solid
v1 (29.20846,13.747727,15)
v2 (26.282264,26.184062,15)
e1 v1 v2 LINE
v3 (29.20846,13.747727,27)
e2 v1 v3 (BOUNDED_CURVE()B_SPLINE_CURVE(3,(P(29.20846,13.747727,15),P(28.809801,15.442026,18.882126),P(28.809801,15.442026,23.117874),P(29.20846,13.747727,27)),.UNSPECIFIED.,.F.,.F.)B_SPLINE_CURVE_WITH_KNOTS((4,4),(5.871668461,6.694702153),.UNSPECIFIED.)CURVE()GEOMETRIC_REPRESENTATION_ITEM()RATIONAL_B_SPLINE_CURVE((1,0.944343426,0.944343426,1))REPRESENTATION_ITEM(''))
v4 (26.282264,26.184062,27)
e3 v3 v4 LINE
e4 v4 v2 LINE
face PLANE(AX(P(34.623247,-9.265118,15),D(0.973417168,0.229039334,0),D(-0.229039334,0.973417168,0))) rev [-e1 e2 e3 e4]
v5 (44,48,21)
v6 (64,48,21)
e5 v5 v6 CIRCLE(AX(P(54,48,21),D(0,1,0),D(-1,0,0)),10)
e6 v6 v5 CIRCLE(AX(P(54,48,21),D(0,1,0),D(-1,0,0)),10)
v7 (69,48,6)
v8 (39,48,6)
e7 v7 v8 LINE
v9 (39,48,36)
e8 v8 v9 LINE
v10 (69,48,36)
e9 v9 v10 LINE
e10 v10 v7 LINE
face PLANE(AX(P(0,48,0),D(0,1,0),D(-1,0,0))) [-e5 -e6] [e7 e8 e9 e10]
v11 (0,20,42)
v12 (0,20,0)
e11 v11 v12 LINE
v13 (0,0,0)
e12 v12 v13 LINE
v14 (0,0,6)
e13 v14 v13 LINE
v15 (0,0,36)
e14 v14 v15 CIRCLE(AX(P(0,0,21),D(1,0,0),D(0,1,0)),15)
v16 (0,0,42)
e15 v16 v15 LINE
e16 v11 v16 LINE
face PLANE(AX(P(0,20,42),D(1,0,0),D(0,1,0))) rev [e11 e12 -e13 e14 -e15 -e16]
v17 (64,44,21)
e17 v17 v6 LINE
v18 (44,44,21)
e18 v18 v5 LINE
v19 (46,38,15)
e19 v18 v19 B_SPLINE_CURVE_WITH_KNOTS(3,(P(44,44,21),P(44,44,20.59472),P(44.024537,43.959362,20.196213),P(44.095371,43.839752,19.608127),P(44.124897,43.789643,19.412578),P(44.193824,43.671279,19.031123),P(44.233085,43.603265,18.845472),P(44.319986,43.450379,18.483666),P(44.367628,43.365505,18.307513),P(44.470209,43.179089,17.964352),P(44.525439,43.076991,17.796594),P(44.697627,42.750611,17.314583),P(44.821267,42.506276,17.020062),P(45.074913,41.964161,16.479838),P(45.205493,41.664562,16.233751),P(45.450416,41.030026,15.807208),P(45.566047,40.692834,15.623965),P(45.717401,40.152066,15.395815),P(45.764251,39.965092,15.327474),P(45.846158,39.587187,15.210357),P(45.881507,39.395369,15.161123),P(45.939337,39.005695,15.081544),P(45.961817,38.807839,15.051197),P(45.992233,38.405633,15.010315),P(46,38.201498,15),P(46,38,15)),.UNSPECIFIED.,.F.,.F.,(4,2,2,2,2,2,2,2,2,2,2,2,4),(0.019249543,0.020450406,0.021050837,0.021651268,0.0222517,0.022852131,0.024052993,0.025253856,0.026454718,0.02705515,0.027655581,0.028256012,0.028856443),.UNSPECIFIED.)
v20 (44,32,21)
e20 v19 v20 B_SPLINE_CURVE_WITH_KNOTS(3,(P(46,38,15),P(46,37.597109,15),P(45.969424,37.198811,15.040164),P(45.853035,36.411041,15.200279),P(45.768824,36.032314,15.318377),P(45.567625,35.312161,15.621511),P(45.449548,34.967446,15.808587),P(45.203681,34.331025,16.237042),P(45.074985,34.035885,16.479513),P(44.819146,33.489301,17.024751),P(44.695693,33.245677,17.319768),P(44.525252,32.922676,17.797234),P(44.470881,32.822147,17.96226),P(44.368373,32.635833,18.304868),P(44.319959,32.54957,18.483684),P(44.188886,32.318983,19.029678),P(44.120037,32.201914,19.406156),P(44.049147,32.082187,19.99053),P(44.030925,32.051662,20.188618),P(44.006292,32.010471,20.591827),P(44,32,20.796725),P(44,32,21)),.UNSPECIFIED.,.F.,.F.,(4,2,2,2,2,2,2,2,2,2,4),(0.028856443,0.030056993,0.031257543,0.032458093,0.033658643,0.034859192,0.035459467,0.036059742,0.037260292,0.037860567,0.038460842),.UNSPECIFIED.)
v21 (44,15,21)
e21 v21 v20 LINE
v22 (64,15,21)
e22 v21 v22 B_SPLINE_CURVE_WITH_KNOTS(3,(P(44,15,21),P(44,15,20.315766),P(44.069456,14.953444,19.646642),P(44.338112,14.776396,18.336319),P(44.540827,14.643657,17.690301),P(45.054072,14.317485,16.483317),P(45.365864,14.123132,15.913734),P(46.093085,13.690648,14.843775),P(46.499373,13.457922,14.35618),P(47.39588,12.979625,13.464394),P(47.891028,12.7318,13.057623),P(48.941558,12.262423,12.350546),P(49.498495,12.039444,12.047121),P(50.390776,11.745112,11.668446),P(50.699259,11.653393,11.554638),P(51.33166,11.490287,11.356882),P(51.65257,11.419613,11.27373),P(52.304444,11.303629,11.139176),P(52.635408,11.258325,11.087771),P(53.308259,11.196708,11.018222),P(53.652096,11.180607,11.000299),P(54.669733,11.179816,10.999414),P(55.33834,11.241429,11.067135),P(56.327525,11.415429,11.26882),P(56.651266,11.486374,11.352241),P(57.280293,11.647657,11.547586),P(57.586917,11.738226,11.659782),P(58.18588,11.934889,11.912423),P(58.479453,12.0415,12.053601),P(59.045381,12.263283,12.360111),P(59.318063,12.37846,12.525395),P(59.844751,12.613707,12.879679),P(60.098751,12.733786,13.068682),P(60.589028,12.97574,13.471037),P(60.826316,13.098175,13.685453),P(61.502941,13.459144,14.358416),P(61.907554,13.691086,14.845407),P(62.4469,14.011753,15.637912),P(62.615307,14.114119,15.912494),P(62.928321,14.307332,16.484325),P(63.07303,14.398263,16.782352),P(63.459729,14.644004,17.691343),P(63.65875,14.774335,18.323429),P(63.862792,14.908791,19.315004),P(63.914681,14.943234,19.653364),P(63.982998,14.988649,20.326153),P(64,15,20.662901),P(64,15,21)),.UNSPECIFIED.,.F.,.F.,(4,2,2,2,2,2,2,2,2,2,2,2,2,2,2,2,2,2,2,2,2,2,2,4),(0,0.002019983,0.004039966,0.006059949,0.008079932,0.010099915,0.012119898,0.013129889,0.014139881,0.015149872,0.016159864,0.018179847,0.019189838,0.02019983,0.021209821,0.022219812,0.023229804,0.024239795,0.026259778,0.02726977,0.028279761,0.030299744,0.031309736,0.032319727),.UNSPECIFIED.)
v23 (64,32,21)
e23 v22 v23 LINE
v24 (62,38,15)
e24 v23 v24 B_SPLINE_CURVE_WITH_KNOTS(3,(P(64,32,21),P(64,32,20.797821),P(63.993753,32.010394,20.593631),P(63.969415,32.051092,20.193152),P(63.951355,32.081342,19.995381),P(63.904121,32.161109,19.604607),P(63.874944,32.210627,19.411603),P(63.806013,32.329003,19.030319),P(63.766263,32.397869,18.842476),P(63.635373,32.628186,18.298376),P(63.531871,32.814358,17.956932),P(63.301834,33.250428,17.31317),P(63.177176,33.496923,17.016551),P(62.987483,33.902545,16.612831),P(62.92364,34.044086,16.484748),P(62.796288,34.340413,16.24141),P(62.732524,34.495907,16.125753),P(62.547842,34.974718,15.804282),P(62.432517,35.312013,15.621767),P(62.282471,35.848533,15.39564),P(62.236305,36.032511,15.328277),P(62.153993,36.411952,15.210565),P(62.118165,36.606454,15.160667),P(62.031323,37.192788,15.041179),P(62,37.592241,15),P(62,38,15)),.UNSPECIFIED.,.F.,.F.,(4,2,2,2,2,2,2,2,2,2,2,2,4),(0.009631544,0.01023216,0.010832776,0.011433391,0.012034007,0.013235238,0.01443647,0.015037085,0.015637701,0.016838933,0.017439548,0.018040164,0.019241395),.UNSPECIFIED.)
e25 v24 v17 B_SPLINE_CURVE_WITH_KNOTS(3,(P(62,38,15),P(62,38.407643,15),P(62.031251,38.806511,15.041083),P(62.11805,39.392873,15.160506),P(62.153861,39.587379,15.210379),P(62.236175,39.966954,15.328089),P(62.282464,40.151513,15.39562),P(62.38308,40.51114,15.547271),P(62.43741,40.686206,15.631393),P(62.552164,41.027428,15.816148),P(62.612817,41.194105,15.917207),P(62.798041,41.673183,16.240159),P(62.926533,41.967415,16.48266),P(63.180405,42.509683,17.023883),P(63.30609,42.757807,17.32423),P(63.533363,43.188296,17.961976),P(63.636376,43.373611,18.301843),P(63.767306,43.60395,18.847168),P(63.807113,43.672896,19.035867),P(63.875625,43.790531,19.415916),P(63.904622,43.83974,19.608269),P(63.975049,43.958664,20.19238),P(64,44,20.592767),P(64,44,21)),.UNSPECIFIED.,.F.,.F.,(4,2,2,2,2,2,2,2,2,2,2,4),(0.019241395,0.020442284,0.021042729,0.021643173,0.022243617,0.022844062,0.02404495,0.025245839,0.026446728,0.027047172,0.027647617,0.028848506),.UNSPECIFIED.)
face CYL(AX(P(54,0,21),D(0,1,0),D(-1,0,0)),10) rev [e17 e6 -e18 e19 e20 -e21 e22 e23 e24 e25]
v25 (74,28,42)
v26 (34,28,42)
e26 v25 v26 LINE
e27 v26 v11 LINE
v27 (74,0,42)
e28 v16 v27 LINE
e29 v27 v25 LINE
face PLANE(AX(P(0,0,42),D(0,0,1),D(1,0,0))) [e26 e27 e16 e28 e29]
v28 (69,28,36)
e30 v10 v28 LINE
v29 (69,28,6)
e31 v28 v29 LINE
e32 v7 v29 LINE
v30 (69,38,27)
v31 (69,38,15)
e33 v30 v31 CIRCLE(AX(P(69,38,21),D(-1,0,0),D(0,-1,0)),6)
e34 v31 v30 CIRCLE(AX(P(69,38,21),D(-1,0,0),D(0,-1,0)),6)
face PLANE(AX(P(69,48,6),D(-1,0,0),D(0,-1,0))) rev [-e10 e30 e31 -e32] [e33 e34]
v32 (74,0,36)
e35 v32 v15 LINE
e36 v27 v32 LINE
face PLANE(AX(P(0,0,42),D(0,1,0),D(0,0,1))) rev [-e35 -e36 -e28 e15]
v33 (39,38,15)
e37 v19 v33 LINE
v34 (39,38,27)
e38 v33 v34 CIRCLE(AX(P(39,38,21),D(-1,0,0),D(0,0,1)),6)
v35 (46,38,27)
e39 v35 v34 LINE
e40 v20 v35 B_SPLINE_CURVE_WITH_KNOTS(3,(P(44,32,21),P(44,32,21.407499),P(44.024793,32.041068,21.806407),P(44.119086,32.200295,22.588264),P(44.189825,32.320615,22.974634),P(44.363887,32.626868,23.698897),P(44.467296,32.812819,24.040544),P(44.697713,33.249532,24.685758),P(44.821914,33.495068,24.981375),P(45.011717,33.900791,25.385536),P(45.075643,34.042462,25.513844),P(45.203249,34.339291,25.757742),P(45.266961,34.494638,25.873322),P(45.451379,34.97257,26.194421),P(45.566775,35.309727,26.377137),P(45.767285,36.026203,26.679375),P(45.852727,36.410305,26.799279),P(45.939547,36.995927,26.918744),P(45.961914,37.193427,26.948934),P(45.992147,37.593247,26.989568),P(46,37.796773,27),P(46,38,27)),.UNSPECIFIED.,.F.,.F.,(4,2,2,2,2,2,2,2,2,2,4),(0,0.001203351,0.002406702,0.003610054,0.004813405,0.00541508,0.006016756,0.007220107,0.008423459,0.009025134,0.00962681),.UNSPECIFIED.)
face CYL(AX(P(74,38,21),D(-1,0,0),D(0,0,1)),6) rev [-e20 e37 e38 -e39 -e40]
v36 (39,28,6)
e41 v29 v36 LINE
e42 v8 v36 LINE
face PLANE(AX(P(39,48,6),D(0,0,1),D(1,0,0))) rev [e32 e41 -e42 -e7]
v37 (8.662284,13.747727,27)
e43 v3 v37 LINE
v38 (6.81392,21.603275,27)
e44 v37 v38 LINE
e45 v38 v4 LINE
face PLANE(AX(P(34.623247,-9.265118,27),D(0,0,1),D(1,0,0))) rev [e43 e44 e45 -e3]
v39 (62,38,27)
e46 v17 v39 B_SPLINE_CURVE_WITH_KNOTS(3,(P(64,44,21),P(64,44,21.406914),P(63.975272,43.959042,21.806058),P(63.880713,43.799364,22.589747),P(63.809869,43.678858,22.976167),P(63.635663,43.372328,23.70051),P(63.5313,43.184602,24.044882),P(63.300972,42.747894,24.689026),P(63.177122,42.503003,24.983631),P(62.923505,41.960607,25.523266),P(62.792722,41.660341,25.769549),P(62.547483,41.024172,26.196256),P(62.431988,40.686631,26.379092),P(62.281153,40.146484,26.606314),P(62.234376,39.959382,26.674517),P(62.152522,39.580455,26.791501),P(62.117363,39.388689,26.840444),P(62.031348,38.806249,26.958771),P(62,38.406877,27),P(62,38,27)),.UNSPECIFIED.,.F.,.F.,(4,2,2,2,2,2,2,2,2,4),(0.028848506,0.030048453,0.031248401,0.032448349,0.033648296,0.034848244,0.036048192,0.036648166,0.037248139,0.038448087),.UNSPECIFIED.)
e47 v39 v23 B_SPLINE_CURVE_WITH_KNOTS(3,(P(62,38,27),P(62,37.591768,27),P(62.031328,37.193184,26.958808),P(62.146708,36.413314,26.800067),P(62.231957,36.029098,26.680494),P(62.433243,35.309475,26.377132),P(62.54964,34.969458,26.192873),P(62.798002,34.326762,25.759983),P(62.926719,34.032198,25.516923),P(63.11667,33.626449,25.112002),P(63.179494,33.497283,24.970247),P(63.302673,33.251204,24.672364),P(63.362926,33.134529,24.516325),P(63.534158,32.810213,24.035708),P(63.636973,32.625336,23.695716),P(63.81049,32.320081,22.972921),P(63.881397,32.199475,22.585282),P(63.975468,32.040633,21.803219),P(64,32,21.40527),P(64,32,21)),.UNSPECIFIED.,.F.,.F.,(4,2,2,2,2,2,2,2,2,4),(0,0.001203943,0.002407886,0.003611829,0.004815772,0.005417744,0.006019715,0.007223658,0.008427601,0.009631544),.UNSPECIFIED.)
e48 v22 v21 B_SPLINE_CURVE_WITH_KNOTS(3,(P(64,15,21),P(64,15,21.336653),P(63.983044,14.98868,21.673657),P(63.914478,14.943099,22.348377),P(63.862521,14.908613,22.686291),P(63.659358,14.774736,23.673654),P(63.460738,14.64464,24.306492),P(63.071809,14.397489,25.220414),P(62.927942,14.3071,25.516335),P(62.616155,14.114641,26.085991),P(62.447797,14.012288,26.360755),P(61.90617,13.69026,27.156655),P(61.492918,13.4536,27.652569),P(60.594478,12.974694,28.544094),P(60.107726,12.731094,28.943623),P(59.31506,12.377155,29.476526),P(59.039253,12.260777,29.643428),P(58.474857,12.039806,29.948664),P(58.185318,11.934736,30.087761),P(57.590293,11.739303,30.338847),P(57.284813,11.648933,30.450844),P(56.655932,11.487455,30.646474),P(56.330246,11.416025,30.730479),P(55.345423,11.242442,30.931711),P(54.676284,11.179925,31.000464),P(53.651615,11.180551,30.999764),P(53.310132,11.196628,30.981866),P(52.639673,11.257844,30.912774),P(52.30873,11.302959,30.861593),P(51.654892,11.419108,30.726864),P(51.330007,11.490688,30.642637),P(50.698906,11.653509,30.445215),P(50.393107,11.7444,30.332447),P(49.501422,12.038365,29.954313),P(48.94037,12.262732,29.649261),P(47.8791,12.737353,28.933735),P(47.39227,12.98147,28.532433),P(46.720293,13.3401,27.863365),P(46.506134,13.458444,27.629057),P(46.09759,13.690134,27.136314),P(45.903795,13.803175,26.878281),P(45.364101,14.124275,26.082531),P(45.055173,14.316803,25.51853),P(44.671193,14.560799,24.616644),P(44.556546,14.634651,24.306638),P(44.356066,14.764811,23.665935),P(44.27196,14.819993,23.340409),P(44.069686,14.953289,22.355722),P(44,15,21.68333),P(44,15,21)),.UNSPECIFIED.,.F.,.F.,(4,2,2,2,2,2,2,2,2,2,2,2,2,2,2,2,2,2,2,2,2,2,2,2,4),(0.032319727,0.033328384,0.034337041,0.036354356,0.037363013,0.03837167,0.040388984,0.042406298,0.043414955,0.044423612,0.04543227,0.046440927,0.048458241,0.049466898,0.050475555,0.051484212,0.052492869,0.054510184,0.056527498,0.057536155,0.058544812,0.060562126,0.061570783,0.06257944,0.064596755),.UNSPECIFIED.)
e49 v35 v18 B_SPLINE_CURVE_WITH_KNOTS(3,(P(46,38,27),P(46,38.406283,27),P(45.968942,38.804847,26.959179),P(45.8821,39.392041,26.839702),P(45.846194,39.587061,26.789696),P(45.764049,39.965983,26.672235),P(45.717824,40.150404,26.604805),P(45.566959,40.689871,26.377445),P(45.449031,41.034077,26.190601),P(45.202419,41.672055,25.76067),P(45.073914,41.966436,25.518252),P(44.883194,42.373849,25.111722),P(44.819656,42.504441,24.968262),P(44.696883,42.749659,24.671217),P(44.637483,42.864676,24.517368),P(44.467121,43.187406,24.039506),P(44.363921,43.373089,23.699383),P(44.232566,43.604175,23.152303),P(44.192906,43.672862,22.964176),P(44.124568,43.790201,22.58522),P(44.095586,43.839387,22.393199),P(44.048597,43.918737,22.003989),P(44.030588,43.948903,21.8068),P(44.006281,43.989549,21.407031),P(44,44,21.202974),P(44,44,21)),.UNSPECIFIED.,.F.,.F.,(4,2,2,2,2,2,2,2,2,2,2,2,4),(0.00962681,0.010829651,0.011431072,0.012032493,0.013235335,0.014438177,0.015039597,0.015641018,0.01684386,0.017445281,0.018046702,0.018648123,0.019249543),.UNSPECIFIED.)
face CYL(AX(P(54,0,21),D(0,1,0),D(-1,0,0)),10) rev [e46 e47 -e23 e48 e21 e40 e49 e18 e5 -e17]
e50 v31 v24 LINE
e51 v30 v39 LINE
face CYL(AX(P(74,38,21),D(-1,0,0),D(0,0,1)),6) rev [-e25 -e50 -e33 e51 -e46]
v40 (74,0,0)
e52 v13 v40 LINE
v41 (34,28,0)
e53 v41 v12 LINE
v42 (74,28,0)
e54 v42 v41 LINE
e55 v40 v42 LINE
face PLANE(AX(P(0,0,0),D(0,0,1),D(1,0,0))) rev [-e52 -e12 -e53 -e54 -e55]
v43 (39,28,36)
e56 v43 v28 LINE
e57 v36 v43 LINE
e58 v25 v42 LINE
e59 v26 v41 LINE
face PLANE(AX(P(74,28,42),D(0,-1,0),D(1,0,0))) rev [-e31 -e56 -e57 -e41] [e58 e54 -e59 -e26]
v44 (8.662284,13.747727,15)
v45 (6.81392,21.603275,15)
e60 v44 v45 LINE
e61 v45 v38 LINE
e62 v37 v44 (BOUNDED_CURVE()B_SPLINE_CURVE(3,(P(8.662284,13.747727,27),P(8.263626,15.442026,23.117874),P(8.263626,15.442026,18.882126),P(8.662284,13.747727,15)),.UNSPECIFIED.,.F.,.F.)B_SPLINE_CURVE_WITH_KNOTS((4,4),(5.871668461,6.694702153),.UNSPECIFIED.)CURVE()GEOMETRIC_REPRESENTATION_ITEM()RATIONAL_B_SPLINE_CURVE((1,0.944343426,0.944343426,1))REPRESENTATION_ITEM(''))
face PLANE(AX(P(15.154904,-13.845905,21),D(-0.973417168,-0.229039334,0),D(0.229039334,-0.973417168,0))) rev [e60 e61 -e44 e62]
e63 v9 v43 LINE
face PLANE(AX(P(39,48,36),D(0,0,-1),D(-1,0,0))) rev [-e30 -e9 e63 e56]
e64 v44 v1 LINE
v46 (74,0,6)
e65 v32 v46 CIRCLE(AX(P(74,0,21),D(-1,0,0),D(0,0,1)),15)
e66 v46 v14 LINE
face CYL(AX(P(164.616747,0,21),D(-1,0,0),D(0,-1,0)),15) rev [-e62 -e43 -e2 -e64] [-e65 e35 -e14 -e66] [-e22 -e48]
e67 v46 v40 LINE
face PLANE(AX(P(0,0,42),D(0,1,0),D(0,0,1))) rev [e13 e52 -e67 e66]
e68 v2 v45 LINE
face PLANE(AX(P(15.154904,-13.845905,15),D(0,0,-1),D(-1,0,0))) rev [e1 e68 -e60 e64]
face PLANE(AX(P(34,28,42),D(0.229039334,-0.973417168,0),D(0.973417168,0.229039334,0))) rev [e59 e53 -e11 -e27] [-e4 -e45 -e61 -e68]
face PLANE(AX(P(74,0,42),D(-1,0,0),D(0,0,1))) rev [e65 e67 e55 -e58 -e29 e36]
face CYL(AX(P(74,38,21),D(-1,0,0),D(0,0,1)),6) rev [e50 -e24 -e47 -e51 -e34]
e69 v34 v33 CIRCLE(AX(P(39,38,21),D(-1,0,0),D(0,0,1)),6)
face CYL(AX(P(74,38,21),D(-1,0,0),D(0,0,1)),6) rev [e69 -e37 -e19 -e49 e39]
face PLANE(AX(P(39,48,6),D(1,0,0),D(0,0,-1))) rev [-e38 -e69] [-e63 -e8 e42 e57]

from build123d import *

# Parameters (mm, degrees)
BASE_BLOCK_DEPTH       = 42
TOP_BOSS_SKETCH_W      = 30
TOP_BOSS_SKETCH_H      = 30
TOP_BOSS_30X30_DEPTH   = 20
VERTICAL_BORE_SKETCH_R = 10
VERTICAL_BORE_DEPTH    = 98.693397935
CROSS_HOLE_SKETCH_R    = 6
CROSS_HOLE_DEPTH       = 75.759614766
ANGLED_POCKET_DEPTH    = 94.61448679
ARCH_CUTOUT_DEPTH      = 98.693397984
ARCH_CUTOUT_DEPTH_BACK = 98.693397984


with BuildPart() as part:
    # Base Block Profile Sketch → Base Block (new body)
    with BuildSketch(Plane.XY):
        Polygon((0, 0), (74, 0), (74, 28), (34, 28), (0, 20), align=None)
    extrude(amount=BASE_BLOCK_DEPTH)

    # Top Boss Sketch → Top Boss 30x30 (add)
    with BuildSketch(Plane(origin=(0, 28, 0), x_dir=(1, 0, 0), z_dir=(0, 1, 0))):
        with Locations((54, -21)):
            Rectangle(TOP_BOSS_SKETCH_W, TOP_BOSS_SKETCH_H)
    extrude(amount=TOP_BOSS_30X30_DEPTH)

    # Vertical Bore Sketch → Vertical Bore (cut, through all)
    with BuildSketch(Plane(origin=(0, 48, 0), x_dir=(1, 0, 0), z_dir=(0, 1, 0))):
        with Locations(Location((54, -21, 0), (0, 0, 180))):
            Circle(VERTICAL_BORE_SKETCH_R)
    extrude(amount=-VERTICAL_BORE_DEPTH, mode=Mode.SUBTRACT)

    # Cross Hole Sketch → Cross Hole (cut, through all)
    with BuildSketch(Plane.ZY.offset(-39)):
        with Locations((21, 38)):
            Circle(CROSS_HOLE_SKETCH_R)
    extrude(amount=-CROSS_HOLE_DEPTH, mode=Mode.SUBTRACT)

    # Angled Pocket Sketch → Angled Pocket (cut, through all)
    with BuildSketch(Plane(origin=(-4.459016393, 18.950819672, 0), x_dir=(0.973417168333576, 0.22903933372554744, 0), z_dir=(-0.22903933372554744, 0.973417168333576, 0))):
        Polygon((11.580786675, -21), (11.580786675, -15), (31.580786675, -15), (31.580786675, -27), (11.580786675, -27), align=None)
    extrude(amount=-ANGLED_POCKET_DEPTH, mode=Mode.SUBTRACT)

    # Arch Cutout Sketch → Arch Cutout (cut, two sides: drawn at the far end of the back side and taken through both)
    with BuildSketch(Plane.ZY.offset(-ARCH_CUTOUT_DEPTH_BACK)):
        with BuildLine():
            Line((36, -130.00000016), (36, 0))
            ThreePointArc((36, 0), (21, 15), (6, 0))
            Line((6, 0), (6, -130.00000016))
            Line((6, -130.00000016), (6, -390.00000048))
            Line((6, -390.00000048), (36, -390.00000048))
            Line((36, -390.00000048), (36, -130.00000016))
        make_face()
    extrude(amount=ARCH_CUTOUT_DEPTH + ARCH_CUTOUT_DEPTH_BACK, mode=Mode.SUBTRACT)


solid = part.part
